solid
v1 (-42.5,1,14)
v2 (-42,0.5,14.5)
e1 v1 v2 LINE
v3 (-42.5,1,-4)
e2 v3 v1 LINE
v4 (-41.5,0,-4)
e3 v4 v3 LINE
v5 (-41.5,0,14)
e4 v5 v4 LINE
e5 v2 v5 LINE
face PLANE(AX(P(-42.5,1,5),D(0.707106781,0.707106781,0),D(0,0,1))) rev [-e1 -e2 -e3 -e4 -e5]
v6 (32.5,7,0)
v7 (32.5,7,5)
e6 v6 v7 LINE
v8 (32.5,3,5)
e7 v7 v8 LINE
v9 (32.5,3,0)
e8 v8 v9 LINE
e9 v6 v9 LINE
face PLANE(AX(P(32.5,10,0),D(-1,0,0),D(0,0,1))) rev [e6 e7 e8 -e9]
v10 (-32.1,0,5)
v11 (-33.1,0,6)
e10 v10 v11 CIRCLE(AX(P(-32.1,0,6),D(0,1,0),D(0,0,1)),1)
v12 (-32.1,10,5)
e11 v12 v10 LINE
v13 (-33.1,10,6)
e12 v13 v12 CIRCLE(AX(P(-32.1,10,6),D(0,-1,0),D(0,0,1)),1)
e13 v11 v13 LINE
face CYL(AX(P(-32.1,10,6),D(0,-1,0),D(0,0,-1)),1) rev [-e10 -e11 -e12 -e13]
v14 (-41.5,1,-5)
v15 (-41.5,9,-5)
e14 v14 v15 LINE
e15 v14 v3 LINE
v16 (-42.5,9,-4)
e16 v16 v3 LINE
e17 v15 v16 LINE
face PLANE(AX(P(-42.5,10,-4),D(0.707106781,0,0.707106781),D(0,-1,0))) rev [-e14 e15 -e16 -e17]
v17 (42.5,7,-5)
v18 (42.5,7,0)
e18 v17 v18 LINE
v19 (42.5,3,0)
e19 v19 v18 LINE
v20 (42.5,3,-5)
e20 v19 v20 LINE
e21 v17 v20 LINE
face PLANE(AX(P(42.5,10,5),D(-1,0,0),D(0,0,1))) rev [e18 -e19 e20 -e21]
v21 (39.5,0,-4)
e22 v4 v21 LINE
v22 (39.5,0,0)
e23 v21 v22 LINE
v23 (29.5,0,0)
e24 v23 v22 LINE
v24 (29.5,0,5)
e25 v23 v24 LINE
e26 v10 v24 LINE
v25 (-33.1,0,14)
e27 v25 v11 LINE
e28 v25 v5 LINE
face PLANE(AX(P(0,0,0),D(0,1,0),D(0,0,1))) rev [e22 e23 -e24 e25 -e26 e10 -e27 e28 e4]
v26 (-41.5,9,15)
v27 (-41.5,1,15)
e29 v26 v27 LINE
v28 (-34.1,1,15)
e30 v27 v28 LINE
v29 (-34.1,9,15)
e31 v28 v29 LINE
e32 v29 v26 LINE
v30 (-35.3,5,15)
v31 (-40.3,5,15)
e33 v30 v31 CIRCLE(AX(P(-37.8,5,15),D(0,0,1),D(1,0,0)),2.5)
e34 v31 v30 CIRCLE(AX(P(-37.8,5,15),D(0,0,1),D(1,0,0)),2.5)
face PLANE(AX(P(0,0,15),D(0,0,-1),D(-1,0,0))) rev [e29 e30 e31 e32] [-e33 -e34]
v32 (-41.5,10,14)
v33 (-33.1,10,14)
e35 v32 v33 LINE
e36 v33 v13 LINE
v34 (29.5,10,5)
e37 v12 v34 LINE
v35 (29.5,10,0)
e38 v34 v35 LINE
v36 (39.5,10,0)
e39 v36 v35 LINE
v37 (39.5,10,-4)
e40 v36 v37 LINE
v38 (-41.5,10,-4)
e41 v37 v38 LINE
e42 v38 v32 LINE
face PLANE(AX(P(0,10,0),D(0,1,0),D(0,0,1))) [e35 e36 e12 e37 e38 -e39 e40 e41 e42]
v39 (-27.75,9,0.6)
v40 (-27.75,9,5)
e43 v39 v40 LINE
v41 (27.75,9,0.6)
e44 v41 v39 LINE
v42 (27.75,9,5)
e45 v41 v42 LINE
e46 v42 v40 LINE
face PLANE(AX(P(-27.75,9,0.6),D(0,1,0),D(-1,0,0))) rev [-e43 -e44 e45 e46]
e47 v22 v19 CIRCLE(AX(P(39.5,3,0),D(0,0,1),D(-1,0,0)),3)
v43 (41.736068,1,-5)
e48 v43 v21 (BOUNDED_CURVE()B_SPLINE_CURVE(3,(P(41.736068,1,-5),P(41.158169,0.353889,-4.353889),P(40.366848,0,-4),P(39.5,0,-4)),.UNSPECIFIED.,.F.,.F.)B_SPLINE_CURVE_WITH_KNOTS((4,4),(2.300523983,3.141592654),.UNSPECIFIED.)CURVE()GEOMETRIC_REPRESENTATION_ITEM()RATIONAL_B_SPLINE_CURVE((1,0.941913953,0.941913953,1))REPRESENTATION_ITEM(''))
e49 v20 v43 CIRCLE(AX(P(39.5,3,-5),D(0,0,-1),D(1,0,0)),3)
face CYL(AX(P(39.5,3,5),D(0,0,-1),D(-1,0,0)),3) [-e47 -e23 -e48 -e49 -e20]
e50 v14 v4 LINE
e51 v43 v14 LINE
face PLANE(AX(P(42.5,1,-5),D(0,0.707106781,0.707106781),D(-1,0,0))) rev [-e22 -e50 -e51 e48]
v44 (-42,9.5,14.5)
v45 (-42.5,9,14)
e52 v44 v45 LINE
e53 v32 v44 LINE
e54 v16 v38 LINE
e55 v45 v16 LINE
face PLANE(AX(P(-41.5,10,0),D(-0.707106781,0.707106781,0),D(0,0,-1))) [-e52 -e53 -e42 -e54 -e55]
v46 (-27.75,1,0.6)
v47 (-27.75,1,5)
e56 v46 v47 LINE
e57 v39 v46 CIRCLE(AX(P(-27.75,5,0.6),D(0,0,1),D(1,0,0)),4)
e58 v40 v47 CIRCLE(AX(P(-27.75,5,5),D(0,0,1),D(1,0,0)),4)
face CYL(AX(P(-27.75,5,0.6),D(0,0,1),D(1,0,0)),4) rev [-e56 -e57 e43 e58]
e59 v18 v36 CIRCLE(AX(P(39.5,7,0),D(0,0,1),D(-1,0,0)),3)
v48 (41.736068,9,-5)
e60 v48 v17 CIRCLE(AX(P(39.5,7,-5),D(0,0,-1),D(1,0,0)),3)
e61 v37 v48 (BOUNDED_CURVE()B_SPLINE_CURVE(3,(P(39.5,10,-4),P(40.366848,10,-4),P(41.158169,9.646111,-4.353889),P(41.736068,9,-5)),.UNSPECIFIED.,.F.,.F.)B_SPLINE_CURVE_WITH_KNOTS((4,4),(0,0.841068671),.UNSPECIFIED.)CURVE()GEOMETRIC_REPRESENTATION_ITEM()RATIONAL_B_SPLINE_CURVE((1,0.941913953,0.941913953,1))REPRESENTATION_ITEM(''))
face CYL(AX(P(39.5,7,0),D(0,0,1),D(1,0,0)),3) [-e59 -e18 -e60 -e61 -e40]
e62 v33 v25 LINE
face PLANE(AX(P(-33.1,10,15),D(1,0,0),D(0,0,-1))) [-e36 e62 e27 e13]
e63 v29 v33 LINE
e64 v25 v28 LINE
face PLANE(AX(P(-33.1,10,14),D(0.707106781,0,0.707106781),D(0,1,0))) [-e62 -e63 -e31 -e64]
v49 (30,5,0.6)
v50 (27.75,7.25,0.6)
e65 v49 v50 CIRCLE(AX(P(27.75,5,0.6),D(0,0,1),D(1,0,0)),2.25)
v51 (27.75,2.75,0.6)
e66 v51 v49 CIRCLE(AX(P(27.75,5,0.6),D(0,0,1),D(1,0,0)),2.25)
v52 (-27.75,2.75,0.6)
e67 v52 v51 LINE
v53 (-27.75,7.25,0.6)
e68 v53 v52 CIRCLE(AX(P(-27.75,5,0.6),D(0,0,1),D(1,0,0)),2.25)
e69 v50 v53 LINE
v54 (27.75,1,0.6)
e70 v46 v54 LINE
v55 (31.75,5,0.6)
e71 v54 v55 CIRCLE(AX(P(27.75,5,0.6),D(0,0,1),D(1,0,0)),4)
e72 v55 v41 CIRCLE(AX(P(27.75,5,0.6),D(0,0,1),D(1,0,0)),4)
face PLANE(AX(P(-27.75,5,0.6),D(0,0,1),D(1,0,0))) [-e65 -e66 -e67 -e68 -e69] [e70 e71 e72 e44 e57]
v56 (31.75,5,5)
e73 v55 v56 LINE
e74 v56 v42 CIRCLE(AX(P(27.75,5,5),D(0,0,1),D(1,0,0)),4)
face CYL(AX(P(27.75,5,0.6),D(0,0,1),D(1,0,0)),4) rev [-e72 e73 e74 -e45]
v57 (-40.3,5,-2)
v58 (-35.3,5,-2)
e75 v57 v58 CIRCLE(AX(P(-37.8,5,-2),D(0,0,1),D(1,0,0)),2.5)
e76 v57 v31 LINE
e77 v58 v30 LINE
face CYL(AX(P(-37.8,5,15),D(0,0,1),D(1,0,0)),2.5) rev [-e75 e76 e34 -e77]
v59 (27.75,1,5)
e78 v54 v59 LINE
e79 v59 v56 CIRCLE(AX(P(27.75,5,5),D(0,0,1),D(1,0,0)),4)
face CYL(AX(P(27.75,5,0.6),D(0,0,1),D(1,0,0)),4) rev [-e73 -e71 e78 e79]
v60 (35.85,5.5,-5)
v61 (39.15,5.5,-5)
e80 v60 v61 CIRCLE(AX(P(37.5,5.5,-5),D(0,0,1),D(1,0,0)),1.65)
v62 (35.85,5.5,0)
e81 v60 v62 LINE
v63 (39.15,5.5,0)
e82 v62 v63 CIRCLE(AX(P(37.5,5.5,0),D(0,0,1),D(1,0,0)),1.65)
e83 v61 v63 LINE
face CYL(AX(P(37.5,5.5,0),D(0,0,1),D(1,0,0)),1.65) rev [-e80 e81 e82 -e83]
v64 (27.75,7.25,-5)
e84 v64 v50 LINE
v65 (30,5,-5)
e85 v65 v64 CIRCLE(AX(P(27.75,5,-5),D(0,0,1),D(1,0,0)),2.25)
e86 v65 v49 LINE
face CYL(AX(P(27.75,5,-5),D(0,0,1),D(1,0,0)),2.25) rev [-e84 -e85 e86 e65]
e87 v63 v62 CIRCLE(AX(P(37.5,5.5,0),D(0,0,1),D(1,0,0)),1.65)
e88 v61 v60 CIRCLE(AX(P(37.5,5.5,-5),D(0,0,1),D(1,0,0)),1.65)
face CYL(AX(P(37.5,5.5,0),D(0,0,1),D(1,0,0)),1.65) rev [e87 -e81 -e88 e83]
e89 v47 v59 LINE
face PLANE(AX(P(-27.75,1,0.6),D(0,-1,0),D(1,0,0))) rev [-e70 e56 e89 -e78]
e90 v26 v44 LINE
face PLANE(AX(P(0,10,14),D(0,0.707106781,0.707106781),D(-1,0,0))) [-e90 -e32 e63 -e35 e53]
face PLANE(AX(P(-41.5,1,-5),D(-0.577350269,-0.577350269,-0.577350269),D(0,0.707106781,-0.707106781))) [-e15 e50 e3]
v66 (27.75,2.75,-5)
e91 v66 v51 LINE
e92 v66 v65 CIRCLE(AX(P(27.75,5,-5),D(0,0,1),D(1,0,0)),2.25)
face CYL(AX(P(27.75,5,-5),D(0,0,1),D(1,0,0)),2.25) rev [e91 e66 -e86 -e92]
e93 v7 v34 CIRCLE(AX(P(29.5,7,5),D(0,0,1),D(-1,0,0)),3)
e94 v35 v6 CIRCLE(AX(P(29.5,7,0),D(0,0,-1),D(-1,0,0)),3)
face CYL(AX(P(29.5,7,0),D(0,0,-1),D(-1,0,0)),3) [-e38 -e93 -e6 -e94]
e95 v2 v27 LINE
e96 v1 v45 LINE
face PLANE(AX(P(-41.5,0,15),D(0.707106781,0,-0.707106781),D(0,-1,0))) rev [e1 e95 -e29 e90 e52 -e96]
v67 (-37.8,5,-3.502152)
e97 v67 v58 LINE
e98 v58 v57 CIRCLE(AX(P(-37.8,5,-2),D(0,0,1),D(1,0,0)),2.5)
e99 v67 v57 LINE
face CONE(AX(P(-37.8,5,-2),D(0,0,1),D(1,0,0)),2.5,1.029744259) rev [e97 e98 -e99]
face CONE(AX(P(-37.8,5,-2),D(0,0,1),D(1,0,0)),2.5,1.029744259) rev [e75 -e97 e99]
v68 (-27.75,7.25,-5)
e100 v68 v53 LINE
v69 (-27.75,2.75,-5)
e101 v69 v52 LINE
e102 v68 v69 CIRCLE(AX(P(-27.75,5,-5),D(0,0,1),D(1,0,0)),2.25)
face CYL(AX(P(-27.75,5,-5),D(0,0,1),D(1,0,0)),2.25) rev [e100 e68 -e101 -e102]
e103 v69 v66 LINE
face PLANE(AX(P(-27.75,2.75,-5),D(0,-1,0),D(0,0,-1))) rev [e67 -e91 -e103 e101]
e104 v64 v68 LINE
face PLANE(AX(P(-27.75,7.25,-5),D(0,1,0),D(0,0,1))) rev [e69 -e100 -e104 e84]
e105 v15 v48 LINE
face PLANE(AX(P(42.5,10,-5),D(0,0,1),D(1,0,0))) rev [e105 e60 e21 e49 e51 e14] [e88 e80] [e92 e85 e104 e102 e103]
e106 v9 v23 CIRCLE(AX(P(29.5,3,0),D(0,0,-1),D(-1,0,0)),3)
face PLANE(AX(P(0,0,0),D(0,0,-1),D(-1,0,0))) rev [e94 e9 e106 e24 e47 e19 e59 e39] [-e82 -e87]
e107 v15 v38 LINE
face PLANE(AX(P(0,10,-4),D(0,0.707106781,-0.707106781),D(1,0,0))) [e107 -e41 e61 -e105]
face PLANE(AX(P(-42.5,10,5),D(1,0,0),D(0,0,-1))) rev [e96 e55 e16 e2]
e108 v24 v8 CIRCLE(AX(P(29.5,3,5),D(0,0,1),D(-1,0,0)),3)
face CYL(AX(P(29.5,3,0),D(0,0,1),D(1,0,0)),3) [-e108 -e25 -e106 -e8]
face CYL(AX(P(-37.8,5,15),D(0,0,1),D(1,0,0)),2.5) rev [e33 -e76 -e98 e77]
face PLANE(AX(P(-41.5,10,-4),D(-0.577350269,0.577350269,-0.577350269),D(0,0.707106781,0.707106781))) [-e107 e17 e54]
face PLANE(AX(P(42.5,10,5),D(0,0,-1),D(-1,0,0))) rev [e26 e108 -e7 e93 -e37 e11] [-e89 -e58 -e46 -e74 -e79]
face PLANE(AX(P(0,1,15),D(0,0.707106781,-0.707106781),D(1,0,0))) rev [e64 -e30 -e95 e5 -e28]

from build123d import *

# Parameters (mm, degrees)
SKETCH1_W             = 85
SKETCH1_H             = 10
BOSS_EXTRUDE1_DEPTH   = 10
CUT_EXTRUDE1_DEPTH    = 4.4
CUT_EXTRUDE2_DEPTH    = 45.018291652
SKETCH4_W             = 9.4
SKETCH4_H             = 10
BOSS_EXTRUDE2_DEPTH   = 10
SKETCH5_W             = 10
SKETCH5_H             = 10
CUT_EXTRUDE3_DEPTH    = 5
M6_TAPPED_HOLE1_D     = 5
M6_TAPPED_HOLE1_DEPTH = 17
M6_TAPPED_HOLE1_TIP   = 1.502151548
M4_TAPPED_HOLE1_D     = 3.3
M4_TAPPED_HOLE1_DEPTH = 11.5
M4_TAPPED_HOLE1_TIP   = 0.991420021
FILLET1_R             = 3
CHAMFER2_SIZE         = 1
FILLET2_R             = 1
CHAMFER3_SIZE         = 1
FILLET3_R             = 3


with BuildPart() as part:
    # Sketch1 → Boss-Extrude1 (new body)
    with BuildSketch(Plane(origin=(0, 0, 0), x_dir=(1, 0, 0), z_dir=(0, 1, 0))):
        Rectangle(SKETCH1_W, SKETCH1_H)
    extrude(amount=BOSS_EXTRUDE1_DEPTH)

    # Sketch2 → Cut-Extrude1 (cut)
    with BuildSketch(Plane.XY.offset(5)):
        with BuildLine():
            Line((-27.75, 9), (27.75, 9))
            ThreePointArc((27.75, 9), (31.75, 5), (27.75, 1))
            Line((27.75, 1), (-27.75, 1))
            ThreePointArc((-27.75, 1), (-31.75, 5), (-27.75, 9))
        make_face()
    extrude(amount=-CUT_EXTRUDE1_DEPTH, mode=Mode.SUBTRACT)

    # Sketch3 → Cut-Extrude2 (cut, through all)
    with BuildSketch(Plane.XY.offset(0.6)):
        with BuildLine():
            Line((-27.75, 7.25), (27.75, 7.25))
            ThreePointArc((27.75, 7.25), (30, 5), (27.75, 2.75))
            Line((27.75, 2.75), (-27.75, 2.75))
            ThreePointArc((-27.75, 2.75), (-30, 5), (-27.75, 7.25))
        make_face()
    extrude(amount=-CUT_EXTRUDE2_DEPTH, mode=Mode.SUBTRACT)

    # Sketch4 → Boss-Extrude2 (add)
    with BuildSketch(Plane.XY.offset(5)):
        with Locations((-37.8, 5)):
            Rectangle(SKETCH4_W, SKETCH4_H)
    extrude(amount=BOSS_EXTRUDE2_DEPTH)

    # Sketch5 → Cut-Extrude3 (cut)
    with BuildSketch(Plane.XY.offset(5)):
        with Locations((37.5, 5)):
            Rectangle(SKETCH5_W, SKETCH5_H)
    extrude(amount=-CUT_EXTRUDE3_DEPTH, mode=Mode.SUBTRACT)

    # M6 Tapped Hole1
    with Locations(Plane.XY.offset(15)):
        with Locations((-37.8, 5)):
            Hole(M6_TAPPED_HOLE1_D / 2, depth=M6_TAPPED_HOLE1_DEPTH)
            with Locations((0, 0, -(M6_TAPPED_HOLE1_DEPTH + M6_TAPPED_HOLE1_TIP / 2))):  # 118° drill point
                Cone(0, M6_TAPPED_HOLE1_D / 2, M6_TAPPED_HOLE1_TIP, mode=Mode.SUBTRACT)

    # M4 Tapped Hole1
    with Locations(Plane.XY):
        with Locations((37.5, 5.5)):
            Hole(M4_TAPPED_HOLE1_D / 2, depth=M4_TAPPED_HOLE1_DEPTH)
            with Locations((0, 0, -(M4_TAPPED_HOLE1_DEPTH + M4_TAPPED_HOLE1_TIP / 2))):  # 118° drill point
                Cone(0, M4_TAPPED_HOLE1_D / 2, M4_TAPPED_HOLE1_TIP, mode=Mode.SUBTRACT)

    # Fillet1
    fillet1_edges = [part.edges().sort_by_distance(p)[0] for p in [
        (32.5, 0, 2.5),
        (32.5, 10, 2.5),
    ]]
    fillet(fillet1_edges, radius=FILLET1_R)

    # Chamfer2
    chamfer2_edges = [part.edges().sort_by_distance(p)[0] for p in [
        (-37.8, 10, 15),
        (-33.1, 5, 15),
        (-42.5, 5, 15),
        (-37.8, 0, 15),
    ]]
    chamfer(chamfer2_edges, length=CHAMFER2_SIZE)

    # Fillet2
    fillet2_edges = [part.edges().sort_by_distance(p)[0] for p in [
        (-33.1, 5, 5),
    ]]
    fillet(fillet2_edges, radius=FILLET2_R)

    # Chamfer3
    chamfer3_edges = [part.edges().sort_by_distance(p)[0] for p in [
        (0, 10, -5),
        (-42.5, 10, 4.5),
        (0, 0, -5),
        (-42.5, 0, 4.5),
        (-42.5, 5, -5),
    ]]
    chamfer(chamfer3_edges, length=CHAMFER3_SIZE)

    # Fillet3
    fillet3_edges = [part.edges().sort_by_distance(p)[0] for p in [
        (42.5, 0, -2),
        (42.5, 10, -2),
    ]]
    fillet(fillet3_edges, radius=FILLET3_R)


solid = part.part
